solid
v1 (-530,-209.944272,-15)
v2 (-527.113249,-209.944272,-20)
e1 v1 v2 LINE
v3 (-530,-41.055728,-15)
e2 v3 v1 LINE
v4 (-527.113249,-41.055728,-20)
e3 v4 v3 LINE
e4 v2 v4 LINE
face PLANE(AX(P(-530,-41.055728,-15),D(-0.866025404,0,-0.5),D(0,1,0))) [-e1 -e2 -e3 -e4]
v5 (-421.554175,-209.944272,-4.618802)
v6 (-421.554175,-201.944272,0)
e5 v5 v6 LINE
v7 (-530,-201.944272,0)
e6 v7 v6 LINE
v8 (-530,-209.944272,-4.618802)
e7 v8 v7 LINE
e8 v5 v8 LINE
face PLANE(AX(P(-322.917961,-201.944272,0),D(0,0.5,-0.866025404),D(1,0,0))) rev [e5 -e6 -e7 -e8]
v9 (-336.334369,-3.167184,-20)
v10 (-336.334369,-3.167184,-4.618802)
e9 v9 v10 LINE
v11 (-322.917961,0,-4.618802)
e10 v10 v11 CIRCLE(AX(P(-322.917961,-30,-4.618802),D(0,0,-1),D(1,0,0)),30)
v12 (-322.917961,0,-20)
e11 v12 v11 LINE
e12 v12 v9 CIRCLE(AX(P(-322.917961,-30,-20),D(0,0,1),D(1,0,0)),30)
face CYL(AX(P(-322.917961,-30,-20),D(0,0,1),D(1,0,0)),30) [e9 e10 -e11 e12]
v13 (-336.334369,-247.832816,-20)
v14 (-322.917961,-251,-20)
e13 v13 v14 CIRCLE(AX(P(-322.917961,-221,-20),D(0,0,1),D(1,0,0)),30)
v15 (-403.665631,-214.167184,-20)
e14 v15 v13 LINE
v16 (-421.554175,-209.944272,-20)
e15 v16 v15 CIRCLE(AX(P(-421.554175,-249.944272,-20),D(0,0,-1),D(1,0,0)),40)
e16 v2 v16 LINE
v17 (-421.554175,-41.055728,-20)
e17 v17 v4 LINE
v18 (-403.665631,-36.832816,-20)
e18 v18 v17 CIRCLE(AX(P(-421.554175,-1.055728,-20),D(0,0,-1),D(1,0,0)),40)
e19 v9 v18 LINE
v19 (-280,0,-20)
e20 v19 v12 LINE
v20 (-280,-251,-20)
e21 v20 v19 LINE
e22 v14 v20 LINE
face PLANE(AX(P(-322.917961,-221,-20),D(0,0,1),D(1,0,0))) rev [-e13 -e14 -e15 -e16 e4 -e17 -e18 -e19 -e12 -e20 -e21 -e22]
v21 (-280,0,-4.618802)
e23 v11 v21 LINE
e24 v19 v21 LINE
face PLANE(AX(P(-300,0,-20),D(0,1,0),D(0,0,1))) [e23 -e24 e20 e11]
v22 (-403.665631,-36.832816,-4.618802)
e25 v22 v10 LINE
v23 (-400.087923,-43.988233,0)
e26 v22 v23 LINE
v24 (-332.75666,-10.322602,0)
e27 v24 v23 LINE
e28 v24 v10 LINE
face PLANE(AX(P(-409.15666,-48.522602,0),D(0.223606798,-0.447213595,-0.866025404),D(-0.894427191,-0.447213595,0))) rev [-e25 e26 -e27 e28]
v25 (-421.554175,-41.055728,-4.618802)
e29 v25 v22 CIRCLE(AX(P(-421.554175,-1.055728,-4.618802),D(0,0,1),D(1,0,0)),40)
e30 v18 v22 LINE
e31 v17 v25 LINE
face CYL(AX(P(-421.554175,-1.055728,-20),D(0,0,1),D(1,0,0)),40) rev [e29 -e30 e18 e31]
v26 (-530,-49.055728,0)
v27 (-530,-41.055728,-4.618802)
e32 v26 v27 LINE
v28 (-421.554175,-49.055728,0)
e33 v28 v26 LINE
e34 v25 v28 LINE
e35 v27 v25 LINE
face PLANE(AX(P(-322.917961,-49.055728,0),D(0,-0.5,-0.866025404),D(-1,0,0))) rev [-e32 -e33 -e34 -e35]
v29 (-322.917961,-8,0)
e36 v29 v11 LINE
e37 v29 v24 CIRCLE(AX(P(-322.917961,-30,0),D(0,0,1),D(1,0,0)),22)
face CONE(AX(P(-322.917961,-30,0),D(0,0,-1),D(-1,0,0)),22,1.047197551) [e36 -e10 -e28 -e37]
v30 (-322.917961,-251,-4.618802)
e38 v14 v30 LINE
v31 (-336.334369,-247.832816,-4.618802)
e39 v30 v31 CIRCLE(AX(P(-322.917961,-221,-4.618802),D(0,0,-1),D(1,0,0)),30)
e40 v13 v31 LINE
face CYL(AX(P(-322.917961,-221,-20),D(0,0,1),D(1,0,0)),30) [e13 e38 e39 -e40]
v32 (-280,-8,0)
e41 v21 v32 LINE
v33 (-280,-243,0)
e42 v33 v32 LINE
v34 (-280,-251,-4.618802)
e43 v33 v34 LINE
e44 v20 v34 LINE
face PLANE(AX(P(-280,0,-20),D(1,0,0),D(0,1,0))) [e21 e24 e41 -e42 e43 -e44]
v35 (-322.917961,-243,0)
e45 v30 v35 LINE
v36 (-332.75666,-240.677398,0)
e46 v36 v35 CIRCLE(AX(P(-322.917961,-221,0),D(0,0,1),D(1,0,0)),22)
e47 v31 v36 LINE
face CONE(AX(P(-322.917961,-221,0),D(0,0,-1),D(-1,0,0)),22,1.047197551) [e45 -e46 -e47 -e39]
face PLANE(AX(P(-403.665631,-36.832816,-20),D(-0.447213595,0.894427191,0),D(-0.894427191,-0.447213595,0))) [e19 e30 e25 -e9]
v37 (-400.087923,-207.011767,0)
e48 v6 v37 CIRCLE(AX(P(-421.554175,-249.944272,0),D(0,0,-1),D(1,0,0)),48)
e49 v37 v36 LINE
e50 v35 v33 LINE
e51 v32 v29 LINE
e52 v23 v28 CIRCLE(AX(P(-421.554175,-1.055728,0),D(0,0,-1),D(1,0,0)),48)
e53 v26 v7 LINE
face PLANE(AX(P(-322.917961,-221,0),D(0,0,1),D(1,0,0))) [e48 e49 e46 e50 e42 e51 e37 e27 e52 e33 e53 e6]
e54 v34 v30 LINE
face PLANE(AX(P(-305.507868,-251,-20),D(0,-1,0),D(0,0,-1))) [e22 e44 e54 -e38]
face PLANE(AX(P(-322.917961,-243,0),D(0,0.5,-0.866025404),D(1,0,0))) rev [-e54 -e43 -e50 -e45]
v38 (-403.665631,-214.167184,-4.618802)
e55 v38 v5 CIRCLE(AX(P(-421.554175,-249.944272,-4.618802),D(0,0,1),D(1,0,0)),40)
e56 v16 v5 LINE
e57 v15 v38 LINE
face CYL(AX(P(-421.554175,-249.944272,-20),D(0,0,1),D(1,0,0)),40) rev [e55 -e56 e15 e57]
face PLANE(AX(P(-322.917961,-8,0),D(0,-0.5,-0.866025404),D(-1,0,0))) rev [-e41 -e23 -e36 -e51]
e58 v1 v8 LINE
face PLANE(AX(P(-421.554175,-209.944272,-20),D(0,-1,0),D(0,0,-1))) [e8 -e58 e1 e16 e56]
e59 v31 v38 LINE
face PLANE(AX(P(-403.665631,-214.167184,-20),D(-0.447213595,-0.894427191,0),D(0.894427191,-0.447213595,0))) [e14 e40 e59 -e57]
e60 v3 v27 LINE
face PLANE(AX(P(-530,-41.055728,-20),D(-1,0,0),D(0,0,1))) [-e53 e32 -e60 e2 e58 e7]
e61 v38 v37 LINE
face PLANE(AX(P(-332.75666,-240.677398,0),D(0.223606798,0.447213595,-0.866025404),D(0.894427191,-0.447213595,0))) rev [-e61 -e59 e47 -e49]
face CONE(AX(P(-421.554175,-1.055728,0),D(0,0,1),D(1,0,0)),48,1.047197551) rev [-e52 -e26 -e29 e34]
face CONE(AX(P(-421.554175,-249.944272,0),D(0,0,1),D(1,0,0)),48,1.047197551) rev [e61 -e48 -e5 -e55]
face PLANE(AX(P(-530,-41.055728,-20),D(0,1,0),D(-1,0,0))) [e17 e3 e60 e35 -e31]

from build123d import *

# Parameters (mm, degrees)
EXTRUDE_1_DEPTH = 20
CHAMFER_1_SIZE  = 8
CHAMFER_1_SIZE2 = 4.618802154
CHAMFER_3_SIZE  = 5
CHAMFER_3_SIZE2 = 2.886751346


with BuildPart() as part:
    # 草图1 → 凸台-拉伸1 (new body)
    with BuildSketch(Plane.XY):
        with BuildLine():
            Line((-305.507868128, -251), (-322.917960675, -251))
            ThreePointArc((-322.917960675, -251), (-329.810548291, -250.197469684), (-336.33436854, -247.83281573))
            Line((-336.33436854, -247.83281573), (-403.66563146, -214.16718427))
            ThreePointArc((-403.66563146, -214.16718427), (-412.364058458, -211.014312331), (-421.55417528, -209.94427191))
            Line((-421.55417528, -209.94427191), (-530, -209.94427191))
            Line((-530, -209.94427191), (-530, -41.05572809))
            Line((-530, -41.05572809), (-421.55417528, -41.05572809))
            ThreePointArc((-421.55417528, -41.05572809), (-412.364058458, -39.985687669), (-403.66563146, -36.83281573))
            Line((-403.66563146, -36.83281573), (-336.33436854, -3.16718427))
            ThreePointArc((-336.33436854, -3.16718427), (-329.810548291, -0.802530316), (-322.917960675, 0))
            Line((-322.917960675, 0), (-300, 0))
            Line((-300, 0), (-280, 0))
            Line((-280, 0), (-280, -251))
            Line((-280, -251), (-305.507868128, -251))
        make_face()
    extrude(amount=-EXTRUDE_1_DEPTH)

    # 倒角1
    chamfer_1_edges = [part.edges().sort_by_distance(p)[0] for p in [
        (-301.458980338, -251, 0),
        (-329.810548291, -250.197469684, 0),
        (-370, -231, 0),
        (-412.364058458, -211.014312331, 0),
        (-475.77708764, -209.94427191, 0),
        (-475.77708764, -41.05572809, 0),
        (-412.364058458, -39.985687669, 0),
        (-370, -20, 0),
        (-329.810548291, -0.802530316, 0),
        (-301.458980338, 0, 0),
    ]]
    chamfer_1_side = [part.faces().sort_by_distance(p)[0] for p in [
        (-393.523242802, -125.5, 0),
    ]]
    chamfer(chamfer_1_edges, length=CHAMFER_1_SIZE, length2=CHAMFER_1_SIZE2, reference=chamfer_1_side[0])

    # 倒角3
    chamfer_3_edges = [part.edges().sort_by_distance(p)[0] for p in [
        (-530, -125.5, -20),
    ]]
    chamfer_3_side = [part.faces().sort_by_distance(p)[0] for p in [
        (-530, -125.5, -10.093574404),
    ]]
    chamfer(chamfer_3_edges, length=CHAMFER_3_SIZE, length2=CHAMFER_3_SIZE2, reference=chamfer_3_side[0])


solid = part.part
